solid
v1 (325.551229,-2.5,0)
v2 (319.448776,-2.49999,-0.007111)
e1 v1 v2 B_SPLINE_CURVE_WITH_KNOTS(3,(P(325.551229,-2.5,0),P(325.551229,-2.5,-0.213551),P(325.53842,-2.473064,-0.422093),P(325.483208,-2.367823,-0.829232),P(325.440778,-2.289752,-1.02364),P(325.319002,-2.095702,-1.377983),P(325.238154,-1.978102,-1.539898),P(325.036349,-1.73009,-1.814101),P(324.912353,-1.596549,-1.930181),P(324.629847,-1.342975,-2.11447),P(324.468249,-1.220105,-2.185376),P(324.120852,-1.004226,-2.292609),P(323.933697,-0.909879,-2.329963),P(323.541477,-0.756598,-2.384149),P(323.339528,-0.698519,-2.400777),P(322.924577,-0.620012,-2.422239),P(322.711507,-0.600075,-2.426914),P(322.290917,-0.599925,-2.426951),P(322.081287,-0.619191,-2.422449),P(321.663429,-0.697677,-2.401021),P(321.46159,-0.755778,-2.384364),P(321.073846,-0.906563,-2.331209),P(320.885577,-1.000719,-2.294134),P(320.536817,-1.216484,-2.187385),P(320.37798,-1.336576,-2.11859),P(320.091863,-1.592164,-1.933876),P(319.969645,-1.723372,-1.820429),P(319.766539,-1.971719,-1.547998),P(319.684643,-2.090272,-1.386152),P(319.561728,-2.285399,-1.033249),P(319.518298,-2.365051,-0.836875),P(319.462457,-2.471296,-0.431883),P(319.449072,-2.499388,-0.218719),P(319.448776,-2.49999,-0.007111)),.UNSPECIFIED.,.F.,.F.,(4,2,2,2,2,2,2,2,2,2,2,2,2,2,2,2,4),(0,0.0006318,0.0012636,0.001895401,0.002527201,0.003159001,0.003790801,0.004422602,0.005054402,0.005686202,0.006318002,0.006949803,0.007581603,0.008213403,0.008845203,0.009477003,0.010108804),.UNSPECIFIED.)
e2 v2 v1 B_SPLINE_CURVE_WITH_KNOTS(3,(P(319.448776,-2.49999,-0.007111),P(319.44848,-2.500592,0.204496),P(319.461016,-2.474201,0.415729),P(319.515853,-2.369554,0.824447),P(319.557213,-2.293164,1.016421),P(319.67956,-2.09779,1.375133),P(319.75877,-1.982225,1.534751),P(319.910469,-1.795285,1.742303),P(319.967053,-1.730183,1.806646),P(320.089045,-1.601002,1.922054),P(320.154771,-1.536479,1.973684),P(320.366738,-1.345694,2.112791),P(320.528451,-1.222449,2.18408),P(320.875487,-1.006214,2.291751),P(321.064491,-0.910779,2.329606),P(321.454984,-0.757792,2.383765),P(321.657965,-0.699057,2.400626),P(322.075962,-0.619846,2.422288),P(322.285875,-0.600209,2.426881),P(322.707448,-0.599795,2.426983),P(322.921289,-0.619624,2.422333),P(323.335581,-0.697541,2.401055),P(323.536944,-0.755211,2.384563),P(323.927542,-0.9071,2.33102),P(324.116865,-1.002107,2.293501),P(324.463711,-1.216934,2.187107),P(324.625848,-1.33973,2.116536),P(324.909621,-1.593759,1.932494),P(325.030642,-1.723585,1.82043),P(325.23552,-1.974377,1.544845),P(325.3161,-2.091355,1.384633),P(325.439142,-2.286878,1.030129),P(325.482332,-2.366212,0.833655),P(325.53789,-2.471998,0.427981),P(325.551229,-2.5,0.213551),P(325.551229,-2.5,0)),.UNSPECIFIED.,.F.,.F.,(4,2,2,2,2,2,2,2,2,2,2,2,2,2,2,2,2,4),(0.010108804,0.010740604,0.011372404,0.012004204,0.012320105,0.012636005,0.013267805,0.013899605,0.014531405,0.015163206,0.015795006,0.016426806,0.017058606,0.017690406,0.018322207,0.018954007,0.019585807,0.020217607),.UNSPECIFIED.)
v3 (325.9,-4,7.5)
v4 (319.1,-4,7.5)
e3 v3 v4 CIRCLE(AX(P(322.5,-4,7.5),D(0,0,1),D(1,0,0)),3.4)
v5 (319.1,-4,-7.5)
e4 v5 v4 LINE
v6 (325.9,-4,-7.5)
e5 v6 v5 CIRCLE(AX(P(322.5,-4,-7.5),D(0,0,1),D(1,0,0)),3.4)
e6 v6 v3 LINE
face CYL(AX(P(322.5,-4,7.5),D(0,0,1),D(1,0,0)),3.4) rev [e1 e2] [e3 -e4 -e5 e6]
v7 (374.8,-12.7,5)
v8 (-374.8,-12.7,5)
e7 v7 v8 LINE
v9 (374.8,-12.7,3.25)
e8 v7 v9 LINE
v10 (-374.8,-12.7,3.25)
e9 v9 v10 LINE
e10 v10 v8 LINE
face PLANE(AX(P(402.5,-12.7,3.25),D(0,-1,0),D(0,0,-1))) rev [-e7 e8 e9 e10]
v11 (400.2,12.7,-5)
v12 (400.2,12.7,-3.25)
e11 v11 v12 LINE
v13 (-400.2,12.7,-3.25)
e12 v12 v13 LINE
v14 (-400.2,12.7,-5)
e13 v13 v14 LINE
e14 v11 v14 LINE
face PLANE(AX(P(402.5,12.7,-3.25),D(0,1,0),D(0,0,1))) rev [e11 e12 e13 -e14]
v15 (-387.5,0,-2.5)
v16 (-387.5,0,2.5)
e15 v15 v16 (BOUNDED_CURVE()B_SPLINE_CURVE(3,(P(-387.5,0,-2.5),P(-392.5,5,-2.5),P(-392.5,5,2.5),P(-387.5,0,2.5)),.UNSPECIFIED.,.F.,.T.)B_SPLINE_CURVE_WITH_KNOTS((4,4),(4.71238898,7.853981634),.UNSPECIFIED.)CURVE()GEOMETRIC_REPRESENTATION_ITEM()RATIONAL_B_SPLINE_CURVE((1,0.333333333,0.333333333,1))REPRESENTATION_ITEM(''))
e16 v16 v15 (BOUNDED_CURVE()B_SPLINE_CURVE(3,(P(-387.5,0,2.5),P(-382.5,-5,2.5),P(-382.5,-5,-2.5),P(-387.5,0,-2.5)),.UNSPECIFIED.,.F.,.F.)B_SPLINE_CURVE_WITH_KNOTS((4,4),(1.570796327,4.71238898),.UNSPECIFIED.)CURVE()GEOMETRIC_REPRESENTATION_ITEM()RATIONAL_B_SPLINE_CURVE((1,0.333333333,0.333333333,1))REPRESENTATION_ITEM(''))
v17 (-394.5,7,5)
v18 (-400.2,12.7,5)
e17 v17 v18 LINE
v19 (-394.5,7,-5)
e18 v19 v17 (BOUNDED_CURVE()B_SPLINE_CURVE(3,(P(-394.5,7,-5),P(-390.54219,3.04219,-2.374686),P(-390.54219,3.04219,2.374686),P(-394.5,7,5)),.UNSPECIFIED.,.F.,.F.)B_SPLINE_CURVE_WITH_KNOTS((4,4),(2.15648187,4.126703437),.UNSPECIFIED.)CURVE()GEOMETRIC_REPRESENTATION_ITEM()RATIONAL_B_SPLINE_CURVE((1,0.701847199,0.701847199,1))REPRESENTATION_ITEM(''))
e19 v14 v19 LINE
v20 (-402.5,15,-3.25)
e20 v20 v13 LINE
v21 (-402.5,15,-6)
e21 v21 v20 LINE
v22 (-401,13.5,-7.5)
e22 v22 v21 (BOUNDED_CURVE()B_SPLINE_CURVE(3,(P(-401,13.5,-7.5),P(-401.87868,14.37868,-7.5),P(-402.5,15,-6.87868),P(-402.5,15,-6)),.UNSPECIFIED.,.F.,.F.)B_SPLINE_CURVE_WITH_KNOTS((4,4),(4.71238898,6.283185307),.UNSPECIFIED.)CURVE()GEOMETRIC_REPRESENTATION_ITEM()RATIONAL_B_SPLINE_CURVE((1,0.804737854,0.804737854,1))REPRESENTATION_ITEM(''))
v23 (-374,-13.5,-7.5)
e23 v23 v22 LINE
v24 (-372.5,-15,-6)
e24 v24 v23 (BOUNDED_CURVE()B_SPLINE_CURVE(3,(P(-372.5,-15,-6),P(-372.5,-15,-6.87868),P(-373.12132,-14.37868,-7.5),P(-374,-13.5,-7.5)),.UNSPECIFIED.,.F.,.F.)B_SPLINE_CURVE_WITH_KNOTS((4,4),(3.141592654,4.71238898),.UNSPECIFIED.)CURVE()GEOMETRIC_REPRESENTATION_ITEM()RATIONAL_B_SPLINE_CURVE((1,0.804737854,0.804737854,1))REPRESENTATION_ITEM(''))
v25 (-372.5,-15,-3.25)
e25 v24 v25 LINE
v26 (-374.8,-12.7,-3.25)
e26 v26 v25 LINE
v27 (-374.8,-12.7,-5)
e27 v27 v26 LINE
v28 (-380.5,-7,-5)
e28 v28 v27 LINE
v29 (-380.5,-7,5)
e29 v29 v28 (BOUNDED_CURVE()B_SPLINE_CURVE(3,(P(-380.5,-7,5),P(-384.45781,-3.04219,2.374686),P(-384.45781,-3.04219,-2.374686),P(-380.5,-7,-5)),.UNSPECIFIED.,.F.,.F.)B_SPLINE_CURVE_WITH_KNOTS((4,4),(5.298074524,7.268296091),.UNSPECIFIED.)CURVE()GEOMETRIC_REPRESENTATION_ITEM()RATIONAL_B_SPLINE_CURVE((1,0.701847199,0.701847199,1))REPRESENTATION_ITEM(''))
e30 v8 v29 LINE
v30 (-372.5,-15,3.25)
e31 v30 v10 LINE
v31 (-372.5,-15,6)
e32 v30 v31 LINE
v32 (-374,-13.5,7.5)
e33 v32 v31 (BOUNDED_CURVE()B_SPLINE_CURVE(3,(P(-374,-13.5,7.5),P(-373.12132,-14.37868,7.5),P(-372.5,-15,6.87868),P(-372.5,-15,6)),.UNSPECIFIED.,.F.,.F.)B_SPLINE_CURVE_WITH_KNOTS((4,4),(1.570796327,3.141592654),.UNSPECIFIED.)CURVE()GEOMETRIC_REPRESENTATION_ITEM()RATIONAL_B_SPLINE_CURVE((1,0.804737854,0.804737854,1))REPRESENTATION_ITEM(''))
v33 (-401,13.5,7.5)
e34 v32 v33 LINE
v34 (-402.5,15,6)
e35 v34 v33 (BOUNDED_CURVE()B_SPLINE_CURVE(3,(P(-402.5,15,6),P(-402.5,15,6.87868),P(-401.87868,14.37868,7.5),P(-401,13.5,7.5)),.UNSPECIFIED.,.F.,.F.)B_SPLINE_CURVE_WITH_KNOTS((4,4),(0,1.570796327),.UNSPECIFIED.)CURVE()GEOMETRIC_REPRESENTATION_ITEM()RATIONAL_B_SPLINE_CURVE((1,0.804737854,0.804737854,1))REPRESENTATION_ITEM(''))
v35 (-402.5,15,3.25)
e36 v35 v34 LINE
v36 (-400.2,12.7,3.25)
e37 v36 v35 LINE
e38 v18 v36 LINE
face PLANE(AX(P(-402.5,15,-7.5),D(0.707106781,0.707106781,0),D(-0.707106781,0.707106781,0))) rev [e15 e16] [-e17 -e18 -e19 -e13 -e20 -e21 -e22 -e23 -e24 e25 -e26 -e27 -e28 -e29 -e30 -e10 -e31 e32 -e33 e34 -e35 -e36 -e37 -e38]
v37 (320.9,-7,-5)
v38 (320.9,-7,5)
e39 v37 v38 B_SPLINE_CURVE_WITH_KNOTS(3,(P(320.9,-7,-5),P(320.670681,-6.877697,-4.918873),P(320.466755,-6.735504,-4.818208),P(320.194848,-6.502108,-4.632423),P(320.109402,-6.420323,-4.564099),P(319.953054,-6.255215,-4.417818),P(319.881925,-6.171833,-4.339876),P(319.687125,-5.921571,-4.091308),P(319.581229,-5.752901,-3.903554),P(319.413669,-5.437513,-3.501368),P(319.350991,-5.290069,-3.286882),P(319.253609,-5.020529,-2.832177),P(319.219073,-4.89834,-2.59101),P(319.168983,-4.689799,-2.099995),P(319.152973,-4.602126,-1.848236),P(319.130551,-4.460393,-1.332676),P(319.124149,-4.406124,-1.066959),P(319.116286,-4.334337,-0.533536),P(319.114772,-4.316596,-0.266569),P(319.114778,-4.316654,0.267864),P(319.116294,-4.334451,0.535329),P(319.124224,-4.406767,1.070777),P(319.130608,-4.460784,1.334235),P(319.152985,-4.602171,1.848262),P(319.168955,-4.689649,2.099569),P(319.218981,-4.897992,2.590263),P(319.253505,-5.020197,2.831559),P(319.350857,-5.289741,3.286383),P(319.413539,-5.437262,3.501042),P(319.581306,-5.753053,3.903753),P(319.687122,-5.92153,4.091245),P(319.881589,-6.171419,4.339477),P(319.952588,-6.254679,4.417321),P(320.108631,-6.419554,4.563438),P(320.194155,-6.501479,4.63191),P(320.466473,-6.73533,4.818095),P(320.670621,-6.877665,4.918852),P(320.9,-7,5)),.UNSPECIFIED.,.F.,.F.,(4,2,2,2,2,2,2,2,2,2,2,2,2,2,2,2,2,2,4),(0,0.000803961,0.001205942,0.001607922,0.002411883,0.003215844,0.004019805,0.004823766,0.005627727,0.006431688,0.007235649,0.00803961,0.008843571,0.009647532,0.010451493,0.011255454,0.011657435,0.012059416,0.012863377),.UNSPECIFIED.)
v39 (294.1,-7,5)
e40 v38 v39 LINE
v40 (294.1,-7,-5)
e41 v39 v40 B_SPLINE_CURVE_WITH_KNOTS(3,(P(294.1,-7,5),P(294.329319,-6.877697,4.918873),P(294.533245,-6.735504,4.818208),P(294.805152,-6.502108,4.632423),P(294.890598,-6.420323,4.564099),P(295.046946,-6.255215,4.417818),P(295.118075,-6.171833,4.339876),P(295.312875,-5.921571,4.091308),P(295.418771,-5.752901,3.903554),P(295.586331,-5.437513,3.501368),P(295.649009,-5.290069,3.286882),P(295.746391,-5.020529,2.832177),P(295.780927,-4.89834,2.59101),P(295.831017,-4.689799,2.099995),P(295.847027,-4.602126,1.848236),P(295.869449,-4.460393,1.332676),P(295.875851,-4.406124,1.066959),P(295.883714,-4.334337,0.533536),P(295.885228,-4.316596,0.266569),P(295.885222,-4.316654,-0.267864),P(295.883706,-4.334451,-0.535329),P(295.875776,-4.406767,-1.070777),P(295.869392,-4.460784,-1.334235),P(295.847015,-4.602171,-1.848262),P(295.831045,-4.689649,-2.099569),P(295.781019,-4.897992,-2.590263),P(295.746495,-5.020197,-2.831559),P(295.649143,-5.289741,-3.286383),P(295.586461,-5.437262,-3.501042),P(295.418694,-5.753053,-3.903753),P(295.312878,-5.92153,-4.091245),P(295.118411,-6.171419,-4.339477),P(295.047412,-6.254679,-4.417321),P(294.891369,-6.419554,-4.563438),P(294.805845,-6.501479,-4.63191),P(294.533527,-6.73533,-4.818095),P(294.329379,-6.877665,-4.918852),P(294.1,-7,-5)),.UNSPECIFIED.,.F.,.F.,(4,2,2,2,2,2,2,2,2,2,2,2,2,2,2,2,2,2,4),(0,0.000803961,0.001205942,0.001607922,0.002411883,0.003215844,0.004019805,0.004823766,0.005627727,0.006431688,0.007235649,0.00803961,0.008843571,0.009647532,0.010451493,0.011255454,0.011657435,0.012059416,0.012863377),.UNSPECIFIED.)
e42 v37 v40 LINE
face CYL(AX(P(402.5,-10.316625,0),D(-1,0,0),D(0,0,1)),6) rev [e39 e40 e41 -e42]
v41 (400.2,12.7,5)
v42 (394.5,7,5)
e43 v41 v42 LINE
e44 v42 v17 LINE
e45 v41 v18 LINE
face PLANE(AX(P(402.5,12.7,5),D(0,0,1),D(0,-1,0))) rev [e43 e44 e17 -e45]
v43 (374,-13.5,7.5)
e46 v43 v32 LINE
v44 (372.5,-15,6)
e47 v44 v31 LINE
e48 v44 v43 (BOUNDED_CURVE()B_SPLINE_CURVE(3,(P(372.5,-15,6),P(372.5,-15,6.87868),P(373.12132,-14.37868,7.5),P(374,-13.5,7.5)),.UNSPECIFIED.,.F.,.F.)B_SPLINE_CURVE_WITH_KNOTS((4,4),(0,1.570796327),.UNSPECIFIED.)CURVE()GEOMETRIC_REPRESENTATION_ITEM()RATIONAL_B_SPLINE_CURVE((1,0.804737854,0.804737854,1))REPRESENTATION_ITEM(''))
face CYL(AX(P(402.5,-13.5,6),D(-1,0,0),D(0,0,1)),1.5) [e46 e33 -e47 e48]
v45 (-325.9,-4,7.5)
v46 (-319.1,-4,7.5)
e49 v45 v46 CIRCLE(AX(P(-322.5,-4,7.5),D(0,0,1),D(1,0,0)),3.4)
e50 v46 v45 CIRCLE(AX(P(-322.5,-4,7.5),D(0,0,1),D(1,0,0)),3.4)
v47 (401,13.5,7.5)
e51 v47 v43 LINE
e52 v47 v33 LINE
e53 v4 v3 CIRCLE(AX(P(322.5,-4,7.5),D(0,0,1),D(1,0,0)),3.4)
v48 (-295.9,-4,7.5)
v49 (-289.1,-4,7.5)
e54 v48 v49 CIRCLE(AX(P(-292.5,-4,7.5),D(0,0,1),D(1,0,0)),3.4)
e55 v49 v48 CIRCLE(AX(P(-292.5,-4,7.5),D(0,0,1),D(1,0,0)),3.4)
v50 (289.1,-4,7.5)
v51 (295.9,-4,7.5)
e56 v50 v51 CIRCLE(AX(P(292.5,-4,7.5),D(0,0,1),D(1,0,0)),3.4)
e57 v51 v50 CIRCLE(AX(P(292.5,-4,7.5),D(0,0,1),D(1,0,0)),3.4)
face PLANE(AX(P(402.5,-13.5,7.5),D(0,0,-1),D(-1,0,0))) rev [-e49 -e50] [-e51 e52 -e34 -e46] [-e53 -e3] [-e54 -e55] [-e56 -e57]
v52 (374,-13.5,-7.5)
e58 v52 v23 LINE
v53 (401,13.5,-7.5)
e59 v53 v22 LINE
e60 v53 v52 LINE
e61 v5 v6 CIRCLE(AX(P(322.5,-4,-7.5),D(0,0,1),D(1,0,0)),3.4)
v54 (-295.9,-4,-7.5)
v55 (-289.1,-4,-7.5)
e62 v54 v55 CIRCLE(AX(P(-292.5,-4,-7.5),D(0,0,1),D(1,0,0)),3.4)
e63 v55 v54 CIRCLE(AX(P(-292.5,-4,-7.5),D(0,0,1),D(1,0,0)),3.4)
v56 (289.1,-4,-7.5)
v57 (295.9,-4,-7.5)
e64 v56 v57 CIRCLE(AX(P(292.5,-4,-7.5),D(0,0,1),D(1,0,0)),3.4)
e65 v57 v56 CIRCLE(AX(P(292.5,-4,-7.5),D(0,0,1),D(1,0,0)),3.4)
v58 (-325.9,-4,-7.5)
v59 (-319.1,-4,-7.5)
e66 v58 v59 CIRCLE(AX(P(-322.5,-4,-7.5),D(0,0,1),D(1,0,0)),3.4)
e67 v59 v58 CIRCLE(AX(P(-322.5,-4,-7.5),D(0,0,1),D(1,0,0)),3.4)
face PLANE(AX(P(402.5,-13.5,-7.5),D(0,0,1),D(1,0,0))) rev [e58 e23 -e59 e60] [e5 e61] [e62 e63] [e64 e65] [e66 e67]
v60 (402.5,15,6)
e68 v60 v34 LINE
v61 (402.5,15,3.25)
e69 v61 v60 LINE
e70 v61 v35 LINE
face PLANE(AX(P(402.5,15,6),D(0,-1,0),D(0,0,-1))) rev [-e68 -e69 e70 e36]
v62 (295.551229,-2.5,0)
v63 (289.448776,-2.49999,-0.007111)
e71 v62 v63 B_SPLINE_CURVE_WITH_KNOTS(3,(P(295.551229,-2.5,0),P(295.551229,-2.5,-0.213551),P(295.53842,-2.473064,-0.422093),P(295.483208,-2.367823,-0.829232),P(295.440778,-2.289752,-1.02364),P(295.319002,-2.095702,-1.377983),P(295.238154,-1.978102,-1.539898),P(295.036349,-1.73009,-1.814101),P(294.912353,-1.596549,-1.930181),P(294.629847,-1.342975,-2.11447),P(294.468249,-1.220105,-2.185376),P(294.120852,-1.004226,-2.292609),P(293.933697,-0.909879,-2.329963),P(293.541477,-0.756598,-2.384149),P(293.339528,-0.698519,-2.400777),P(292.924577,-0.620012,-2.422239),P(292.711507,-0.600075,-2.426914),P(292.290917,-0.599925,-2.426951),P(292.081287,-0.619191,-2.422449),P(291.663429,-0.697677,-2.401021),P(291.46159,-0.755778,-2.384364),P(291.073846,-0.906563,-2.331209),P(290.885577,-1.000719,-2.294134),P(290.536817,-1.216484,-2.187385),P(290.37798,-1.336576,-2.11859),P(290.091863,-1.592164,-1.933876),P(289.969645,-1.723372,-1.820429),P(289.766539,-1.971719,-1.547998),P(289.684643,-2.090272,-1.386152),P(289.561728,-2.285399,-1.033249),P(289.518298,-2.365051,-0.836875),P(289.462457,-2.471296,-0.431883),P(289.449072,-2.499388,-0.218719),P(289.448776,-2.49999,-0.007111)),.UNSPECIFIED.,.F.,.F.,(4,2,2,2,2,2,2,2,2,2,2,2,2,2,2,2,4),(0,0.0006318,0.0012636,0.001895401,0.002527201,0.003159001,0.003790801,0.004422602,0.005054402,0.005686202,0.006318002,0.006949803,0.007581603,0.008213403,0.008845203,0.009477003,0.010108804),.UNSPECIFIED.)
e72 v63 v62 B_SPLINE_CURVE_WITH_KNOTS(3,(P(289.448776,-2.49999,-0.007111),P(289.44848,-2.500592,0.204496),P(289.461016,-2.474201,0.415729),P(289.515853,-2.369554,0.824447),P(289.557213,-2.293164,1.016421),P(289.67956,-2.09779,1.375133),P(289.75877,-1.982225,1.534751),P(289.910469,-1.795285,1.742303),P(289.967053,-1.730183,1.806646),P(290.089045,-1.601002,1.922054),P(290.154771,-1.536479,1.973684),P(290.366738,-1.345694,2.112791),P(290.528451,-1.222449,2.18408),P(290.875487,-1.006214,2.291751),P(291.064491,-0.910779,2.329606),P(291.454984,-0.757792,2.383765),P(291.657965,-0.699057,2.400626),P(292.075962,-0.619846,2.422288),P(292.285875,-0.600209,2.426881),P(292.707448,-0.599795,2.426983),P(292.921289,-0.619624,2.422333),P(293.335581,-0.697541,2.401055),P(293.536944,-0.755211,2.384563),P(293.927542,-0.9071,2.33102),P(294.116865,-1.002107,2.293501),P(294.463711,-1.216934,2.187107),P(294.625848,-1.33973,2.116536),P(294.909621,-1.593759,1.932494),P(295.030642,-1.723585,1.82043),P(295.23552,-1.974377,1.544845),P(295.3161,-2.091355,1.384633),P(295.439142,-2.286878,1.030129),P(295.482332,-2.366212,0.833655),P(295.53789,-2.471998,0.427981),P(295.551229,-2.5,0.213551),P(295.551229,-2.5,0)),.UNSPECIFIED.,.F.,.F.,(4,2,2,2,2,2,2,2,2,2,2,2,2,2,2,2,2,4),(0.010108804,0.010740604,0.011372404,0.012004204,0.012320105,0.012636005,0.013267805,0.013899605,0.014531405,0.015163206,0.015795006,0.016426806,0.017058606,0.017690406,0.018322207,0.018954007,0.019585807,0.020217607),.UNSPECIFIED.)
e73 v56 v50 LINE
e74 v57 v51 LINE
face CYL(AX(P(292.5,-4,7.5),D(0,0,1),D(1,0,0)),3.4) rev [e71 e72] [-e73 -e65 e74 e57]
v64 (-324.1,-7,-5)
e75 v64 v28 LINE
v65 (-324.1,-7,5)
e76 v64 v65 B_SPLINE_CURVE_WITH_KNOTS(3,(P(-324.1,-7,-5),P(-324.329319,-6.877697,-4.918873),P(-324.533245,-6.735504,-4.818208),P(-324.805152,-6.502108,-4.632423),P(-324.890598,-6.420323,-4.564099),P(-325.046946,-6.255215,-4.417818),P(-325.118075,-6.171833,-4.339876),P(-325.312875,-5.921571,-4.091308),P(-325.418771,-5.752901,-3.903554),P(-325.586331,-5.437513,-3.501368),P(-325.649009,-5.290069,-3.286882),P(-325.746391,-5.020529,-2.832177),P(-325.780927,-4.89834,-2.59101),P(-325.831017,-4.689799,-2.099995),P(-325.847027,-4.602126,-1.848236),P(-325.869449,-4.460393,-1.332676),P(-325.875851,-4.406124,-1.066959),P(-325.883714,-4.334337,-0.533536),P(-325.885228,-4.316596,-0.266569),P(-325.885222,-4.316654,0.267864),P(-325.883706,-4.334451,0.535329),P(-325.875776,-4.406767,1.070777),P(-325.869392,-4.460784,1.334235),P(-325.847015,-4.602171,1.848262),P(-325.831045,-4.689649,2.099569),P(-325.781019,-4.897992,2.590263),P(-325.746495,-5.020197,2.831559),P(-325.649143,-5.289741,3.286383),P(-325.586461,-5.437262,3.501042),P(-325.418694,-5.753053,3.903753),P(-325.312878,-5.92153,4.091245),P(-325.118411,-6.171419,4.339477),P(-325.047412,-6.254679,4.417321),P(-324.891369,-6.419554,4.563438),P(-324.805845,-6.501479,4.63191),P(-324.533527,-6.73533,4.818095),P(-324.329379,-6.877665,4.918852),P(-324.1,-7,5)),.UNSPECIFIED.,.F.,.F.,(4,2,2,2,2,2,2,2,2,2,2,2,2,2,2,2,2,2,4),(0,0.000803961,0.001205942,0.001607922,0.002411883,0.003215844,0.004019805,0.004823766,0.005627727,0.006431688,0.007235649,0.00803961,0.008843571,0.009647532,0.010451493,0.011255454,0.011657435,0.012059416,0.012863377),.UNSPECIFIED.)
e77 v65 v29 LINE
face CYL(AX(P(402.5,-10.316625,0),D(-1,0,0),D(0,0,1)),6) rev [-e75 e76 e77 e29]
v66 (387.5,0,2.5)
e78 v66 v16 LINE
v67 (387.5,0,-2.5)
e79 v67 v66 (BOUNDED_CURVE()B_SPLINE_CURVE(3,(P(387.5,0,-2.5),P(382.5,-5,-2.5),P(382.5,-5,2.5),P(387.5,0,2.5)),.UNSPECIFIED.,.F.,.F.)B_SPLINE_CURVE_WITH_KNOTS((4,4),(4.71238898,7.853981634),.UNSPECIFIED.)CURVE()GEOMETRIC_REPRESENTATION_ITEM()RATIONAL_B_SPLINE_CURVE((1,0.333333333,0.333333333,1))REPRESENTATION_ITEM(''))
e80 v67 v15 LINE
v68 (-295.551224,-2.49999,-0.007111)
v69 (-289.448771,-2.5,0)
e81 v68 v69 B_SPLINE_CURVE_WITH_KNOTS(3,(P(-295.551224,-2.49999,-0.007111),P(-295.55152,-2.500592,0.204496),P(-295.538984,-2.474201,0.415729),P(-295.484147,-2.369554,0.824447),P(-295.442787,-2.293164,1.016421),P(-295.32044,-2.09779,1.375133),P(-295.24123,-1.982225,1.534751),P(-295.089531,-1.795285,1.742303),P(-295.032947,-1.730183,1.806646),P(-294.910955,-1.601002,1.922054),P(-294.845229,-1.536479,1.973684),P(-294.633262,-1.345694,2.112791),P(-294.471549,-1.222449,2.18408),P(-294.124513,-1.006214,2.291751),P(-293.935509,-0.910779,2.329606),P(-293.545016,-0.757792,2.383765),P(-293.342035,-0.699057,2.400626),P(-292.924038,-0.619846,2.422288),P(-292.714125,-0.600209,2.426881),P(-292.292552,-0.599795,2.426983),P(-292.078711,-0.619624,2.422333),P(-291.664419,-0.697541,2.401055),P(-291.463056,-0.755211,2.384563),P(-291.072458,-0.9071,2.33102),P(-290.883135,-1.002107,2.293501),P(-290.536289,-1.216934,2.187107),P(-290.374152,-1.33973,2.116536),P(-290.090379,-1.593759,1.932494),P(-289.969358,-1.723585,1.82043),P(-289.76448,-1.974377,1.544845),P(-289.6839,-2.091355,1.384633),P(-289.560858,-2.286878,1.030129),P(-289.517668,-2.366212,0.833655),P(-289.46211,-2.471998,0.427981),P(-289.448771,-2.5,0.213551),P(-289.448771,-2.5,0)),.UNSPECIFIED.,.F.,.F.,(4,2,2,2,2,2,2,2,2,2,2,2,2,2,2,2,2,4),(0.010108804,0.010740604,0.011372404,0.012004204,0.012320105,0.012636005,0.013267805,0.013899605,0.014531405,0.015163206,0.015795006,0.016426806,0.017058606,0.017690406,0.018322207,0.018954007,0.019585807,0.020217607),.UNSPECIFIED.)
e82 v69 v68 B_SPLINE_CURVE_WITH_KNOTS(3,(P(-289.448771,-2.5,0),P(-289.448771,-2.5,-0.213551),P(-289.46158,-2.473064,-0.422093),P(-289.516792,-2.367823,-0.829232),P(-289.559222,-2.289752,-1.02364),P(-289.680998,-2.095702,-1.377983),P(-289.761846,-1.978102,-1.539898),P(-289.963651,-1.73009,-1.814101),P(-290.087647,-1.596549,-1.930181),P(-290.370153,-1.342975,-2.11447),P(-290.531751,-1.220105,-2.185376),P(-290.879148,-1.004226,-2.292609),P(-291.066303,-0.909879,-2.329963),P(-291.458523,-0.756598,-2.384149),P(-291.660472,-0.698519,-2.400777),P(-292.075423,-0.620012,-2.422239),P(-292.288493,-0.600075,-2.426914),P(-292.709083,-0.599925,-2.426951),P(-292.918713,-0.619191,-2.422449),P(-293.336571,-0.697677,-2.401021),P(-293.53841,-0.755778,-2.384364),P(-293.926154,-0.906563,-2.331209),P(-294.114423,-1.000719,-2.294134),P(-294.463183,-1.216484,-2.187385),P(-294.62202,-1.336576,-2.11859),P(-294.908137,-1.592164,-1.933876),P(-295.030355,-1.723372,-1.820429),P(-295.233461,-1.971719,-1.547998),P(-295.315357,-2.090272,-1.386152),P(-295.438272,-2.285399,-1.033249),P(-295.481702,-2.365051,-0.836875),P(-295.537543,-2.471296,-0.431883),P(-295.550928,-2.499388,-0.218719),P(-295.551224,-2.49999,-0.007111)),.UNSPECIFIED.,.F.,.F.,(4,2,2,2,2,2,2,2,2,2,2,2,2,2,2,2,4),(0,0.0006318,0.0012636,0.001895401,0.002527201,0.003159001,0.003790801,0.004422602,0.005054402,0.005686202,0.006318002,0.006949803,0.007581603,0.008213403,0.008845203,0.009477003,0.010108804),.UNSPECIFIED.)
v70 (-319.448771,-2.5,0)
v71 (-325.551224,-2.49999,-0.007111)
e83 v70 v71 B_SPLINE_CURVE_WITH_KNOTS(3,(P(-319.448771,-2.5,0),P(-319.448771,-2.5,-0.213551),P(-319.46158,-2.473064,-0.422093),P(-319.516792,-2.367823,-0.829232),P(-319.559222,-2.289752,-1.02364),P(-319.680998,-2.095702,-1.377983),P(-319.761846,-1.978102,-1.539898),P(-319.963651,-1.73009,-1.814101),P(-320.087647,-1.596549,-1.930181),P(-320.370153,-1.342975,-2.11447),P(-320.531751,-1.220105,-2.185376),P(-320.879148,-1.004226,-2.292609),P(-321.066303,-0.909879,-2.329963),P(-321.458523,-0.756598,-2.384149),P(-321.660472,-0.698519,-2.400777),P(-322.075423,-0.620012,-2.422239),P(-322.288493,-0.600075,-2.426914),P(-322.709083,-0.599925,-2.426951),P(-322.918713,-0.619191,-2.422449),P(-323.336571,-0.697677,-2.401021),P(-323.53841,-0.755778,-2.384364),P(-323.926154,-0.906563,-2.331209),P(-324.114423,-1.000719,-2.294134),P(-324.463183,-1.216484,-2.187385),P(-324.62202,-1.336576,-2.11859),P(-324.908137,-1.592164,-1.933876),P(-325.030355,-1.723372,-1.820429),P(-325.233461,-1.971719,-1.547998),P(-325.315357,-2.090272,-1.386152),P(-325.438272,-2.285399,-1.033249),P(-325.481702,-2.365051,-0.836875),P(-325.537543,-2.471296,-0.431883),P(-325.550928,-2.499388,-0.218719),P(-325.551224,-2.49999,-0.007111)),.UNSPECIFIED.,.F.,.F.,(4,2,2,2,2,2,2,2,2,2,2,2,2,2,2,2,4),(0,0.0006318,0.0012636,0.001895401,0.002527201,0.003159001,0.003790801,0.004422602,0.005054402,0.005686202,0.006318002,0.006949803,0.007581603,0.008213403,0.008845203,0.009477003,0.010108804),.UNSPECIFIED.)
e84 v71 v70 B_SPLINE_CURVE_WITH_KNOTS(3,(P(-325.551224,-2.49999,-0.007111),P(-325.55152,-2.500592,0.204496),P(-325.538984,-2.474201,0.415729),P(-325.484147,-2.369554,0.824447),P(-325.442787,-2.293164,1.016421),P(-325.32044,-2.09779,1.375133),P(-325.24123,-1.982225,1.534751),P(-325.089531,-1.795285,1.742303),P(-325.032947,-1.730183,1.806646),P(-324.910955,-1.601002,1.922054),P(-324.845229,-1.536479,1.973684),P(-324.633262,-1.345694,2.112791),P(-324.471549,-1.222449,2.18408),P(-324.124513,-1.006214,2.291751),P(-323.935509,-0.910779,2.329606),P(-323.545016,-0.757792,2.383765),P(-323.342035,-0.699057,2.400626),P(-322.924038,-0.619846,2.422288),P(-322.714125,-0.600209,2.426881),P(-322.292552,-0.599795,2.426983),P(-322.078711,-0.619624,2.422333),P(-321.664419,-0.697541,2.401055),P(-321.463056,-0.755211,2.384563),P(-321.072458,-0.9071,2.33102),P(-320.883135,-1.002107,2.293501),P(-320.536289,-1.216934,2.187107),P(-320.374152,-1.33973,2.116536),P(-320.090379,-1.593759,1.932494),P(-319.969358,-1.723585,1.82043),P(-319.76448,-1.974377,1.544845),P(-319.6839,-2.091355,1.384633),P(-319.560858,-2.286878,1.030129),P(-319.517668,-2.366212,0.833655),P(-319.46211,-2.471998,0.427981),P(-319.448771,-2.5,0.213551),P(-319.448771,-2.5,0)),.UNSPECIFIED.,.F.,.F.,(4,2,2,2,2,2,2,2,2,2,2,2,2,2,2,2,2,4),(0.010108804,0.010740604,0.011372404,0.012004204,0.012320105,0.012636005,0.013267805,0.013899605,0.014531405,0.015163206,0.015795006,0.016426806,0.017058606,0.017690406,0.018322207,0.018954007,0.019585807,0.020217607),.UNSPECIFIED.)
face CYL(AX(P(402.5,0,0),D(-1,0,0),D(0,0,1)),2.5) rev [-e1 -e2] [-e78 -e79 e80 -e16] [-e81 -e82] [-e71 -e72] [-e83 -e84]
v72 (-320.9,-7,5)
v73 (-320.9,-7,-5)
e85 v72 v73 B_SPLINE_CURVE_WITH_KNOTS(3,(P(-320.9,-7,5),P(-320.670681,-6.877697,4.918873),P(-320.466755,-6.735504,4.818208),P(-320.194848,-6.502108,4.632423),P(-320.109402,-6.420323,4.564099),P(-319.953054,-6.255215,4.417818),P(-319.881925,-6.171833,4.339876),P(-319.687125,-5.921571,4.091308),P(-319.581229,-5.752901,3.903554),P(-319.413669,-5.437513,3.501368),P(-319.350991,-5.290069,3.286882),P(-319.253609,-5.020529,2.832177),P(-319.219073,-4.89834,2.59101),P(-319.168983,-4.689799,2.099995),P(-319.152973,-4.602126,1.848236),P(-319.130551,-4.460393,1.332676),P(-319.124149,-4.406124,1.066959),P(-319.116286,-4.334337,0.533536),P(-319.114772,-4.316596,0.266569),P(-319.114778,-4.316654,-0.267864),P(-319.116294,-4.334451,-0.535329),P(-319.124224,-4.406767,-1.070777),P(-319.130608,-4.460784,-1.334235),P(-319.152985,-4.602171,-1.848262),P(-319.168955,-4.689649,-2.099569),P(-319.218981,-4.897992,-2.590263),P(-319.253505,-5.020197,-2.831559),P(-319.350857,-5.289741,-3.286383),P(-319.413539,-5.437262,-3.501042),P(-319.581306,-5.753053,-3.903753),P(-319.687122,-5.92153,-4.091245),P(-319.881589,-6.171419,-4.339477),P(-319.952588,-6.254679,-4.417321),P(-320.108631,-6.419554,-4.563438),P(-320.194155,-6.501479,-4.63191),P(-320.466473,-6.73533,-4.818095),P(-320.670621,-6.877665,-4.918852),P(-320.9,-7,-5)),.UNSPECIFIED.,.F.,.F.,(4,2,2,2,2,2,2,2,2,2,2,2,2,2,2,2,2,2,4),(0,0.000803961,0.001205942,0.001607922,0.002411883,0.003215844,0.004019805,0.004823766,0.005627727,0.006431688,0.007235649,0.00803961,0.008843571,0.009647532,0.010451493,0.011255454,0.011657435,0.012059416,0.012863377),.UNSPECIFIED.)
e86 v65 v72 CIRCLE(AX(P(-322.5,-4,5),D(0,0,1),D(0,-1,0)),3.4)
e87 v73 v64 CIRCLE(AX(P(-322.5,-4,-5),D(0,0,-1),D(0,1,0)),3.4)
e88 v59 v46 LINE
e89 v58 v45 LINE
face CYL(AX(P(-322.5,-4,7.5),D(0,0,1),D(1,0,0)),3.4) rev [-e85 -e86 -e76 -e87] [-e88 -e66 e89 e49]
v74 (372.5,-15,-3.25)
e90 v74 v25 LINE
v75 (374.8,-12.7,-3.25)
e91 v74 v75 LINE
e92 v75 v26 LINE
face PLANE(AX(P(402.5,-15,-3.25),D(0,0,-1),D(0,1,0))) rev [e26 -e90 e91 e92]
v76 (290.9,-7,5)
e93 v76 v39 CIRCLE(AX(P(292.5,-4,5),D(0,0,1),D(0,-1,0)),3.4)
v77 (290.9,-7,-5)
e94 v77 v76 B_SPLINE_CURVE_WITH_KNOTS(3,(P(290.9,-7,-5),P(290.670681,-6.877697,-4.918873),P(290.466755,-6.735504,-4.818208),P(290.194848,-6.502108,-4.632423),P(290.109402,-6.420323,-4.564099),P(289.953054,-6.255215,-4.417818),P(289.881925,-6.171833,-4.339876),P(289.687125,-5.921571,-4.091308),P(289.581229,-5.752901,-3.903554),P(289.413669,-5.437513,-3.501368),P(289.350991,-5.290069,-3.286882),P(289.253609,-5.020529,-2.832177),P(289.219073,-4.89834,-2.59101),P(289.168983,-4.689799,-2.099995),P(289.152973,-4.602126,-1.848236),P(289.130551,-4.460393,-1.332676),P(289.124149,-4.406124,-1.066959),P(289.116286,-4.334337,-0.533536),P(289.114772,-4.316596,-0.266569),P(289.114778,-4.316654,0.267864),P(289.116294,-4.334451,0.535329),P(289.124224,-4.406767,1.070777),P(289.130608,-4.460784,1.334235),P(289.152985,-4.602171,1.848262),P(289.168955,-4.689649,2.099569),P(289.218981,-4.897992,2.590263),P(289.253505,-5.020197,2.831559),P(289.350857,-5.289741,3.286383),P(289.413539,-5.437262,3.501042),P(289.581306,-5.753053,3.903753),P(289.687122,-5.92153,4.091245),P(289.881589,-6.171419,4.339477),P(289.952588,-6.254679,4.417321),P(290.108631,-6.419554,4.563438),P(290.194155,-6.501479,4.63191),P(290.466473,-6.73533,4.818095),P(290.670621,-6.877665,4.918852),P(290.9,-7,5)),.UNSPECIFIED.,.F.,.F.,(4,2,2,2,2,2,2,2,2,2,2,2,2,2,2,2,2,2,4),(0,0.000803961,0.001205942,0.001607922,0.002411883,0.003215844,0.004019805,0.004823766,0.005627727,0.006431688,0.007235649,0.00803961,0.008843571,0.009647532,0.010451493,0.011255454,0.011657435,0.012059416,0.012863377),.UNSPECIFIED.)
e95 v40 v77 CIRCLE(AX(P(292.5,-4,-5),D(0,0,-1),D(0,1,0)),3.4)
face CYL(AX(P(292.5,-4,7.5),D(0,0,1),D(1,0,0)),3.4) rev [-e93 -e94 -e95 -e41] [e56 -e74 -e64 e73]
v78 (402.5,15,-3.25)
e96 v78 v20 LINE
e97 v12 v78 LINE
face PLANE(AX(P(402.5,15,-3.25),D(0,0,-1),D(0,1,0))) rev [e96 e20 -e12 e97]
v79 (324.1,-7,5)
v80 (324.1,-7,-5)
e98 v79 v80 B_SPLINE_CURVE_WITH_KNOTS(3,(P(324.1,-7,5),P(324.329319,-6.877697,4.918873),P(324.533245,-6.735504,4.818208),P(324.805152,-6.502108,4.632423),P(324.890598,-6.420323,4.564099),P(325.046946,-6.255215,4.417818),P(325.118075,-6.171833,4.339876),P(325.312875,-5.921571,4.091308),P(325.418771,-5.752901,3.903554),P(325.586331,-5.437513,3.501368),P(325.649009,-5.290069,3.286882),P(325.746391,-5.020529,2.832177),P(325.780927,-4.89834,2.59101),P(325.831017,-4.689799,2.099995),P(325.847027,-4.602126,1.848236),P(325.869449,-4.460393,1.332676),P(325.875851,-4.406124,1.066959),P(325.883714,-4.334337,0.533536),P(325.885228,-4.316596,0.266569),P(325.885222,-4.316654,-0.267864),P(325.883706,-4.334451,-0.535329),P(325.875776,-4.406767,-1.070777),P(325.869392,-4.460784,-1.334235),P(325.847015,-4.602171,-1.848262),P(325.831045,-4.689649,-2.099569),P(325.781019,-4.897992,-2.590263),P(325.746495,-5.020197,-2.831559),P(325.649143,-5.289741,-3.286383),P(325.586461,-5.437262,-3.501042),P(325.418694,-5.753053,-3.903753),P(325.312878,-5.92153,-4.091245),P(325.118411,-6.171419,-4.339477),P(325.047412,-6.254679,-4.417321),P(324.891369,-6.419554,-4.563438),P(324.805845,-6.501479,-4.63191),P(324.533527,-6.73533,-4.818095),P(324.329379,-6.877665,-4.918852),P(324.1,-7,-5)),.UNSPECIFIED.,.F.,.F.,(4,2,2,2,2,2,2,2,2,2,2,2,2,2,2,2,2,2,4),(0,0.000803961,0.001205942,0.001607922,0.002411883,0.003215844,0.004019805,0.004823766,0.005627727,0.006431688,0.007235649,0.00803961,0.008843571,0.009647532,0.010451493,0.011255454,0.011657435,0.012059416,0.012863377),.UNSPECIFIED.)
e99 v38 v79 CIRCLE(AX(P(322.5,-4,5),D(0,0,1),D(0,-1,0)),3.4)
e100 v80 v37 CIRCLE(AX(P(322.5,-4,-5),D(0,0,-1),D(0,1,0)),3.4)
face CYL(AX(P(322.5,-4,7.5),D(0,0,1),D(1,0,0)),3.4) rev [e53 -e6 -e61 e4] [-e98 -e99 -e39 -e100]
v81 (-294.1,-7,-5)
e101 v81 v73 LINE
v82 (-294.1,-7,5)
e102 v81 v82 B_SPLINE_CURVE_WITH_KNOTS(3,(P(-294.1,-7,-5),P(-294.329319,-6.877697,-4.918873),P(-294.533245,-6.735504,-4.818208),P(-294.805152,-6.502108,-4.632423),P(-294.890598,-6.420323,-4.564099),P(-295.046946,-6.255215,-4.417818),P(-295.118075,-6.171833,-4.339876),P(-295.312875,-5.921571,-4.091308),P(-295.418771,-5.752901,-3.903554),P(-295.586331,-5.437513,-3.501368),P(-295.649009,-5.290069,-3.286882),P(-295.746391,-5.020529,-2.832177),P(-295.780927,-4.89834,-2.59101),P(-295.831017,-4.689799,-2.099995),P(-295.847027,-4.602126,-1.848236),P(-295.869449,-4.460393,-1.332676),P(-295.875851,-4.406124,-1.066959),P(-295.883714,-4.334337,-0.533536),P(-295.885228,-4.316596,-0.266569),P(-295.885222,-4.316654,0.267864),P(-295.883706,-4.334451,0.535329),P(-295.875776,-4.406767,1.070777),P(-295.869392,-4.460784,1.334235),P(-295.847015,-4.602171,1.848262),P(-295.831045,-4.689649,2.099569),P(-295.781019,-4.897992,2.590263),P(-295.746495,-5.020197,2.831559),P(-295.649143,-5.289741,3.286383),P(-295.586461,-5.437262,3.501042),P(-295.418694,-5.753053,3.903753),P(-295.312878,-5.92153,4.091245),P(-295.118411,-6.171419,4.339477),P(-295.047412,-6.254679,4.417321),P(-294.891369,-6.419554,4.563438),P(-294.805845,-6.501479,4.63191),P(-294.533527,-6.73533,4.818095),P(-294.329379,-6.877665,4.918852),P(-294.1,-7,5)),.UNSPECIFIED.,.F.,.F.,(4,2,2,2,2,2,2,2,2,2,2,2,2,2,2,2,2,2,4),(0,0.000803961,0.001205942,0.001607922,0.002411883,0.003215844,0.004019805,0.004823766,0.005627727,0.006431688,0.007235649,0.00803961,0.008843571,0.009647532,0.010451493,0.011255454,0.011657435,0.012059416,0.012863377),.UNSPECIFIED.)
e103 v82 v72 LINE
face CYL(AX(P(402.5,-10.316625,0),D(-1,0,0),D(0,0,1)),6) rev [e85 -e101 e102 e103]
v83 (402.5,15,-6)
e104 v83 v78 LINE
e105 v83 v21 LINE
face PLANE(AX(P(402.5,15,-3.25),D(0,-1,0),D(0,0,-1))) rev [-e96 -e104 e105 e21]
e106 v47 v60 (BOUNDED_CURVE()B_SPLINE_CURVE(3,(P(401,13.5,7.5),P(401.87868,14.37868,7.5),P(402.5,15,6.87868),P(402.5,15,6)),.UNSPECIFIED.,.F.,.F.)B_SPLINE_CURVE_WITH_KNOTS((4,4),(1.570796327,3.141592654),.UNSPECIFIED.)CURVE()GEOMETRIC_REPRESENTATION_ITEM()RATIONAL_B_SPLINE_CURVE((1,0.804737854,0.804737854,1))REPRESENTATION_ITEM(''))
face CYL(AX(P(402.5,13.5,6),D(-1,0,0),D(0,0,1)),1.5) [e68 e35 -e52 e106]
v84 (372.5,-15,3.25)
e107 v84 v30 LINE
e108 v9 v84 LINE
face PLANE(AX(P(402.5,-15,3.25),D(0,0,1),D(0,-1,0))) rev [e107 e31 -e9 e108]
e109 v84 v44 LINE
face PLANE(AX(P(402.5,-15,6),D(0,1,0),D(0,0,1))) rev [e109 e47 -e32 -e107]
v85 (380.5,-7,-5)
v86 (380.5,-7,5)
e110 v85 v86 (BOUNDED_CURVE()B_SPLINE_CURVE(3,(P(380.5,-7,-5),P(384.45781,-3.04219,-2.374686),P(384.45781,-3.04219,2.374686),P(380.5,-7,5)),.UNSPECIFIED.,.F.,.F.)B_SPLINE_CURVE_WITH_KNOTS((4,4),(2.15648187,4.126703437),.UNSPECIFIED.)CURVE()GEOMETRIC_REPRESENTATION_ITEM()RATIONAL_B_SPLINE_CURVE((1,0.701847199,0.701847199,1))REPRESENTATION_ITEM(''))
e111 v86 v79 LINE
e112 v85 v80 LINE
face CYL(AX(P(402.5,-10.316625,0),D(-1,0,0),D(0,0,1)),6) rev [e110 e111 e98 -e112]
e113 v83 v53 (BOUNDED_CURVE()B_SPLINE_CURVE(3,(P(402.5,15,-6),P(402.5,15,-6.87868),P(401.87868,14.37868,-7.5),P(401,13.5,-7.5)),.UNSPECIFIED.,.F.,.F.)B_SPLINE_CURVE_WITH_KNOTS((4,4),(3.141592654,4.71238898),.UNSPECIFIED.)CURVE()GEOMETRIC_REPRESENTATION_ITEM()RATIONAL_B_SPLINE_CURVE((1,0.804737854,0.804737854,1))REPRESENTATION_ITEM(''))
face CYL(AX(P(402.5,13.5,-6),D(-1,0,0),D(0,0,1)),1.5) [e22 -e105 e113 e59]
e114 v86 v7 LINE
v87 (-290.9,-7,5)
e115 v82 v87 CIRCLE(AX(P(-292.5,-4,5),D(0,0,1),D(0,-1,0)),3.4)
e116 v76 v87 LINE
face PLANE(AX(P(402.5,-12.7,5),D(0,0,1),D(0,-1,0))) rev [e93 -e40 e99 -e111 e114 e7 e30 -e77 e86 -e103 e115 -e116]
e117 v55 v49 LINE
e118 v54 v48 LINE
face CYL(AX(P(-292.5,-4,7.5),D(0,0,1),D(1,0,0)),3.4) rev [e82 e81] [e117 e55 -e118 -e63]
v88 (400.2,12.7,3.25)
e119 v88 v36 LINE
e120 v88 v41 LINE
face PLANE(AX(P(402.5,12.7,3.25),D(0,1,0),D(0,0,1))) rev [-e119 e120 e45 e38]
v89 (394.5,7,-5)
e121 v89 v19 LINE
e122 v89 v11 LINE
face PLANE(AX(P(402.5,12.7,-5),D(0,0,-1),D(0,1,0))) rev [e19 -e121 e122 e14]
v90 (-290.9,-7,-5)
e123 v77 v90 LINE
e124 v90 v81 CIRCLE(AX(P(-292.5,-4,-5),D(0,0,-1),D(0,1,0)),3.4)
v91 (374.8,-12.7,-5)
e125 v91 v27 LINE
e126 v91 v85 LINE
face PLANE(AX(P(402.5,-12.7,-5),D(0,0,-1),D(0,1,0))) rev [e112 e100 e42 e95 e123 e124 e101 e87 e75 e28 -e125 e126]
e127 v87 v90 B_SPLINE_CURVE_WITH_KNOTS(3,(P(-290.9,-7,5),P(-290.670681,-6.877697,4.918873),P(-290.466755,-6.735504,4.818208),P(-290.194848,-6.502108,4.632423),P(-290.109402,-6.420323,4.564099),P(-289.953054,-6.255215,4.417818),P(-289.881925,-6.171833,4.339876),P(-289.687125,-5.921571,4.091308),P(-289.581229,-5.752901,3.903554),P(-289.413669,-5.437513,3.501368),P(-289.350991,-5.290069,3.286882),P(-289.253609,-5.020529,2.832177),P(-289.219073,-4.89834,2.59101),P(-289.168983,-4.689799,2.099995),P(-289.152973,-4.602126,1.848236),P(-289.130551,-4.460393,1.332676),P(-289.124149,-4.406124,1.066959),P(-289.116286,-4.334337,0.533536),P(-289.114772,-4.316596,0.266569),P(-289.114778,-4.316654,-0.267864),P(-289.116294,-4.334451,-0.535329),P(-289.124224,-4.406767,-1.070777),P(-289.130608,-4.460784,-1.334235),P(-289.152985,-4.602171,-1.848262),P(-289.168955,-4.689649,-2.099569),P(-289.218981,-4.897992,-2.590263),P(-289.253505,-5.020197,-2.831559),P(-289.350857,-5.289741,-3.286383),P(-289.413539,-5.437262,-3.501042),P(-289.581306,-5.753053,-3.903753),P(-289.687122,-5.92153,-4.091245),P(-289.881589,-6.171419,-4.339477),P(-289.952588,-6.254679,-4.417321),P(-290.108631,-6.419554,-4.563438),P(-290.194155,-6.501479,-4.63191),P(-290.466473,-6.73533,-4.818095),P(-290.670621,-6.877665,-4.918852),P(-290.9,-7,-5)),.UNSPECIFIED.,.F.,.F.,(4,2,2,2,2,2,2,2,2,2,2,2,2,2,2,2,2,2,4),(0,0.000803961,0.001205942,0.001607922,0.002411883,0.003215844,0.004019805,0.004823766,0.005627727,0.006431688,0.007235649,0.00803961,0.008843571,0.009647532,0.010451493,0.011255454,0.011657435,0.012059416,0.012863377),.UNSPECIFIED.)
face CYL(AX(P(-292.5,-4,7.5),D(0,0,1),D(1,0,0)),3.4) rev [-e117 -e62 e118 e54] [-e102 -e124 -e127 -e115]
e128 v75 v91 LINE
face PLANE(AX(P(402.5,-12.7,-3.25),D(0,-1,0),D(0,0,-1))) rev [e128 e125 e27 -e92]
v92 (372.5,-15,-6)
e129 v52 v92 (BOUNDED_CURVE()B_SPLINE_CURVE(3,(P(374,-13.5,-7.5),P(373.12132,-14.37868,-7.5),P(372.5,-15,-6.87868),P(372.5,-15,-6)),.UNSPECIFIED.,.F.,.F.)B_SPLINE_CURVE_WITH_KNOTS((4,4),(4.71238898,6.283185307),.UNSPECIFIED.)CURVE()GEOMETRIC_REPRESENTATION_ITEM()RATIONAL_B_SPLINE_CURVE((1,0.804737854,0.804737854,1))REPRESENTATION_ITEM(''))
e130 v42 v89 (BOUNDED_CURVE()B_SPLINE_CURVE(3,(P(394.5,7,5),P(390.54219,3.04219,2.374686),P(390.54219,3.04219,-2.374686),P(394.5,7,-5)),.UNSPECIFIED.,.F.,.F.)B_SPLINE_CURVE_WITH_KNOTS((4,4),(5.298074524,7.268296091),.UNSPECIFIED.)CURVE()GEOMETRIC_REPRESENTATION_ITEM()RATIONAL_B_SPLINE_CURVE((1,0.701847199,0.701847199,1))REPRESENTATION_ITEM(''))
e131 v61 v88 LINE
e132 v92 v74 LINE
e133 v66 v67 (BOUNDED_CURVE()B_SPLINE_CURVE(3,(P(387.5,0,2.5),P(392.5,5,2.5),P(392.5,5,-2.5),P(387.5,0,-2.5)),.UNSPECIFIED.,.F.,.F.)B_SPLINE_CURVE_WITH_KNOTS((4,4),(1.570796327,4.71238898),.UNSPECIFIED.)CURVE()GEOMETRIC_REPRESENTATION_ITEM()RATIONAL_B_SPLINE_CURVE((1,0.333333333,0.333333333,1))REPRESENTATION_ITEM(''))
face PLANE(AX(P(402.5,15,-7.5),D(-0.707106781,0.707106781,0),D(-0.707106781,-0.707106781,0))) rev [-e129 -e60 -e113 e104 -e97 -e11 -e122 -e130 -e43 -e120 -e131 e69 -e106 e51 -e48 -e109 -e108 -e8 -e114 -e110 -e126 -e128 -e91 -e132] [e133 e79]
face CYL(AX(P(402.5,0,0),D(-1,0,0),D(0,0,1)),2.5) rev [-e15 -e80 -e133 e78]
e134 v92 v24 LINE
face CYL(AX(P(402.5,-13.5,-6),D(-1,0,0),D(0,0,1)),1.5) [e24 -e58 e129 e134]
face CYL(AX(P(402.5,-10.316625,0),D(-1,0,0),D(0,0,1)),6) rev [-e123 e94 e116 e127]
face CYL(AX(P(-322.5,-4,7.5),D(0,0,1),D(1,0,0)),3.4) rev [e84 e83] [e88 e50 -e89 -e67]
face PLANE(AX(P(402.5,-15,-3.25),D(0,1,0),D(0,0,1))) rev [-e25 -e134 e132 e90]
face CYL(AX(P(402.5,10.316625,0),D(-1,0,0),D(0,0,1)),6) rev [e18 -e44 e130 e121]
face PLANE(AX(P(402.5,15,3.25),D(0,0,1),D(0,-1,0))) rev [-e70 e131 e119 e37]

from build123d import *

# Parameters (mm, degrees)
SKETCH11_R          = 2.5
MEMBER_1_DEPTH      = 805
CUT_EXTRUDE_1_DEPTH = 404.058618566
HOLE_WIZARD_M8_1_D  = 6.8


with BuildPart() as part:
    # Sketch11 → Member 1 (new body)
    with BuildSketch(Plane(origin=(-402.5, 0, 0), x_dir=(0, 0, -1), z_dir=(1, 0, 0))):
        with BuildLine():
            Line((-6, -15), (-3.25, -15))
            Line((-3.25, -15), (-3.25, -12.7))
            Line((-3.25, -12.7), (-5, -12.7))
            Line((-5, -12.7), (-5, -7))
            ThreePointArc((-5, -7), (0, -4.31662479), (5, -7))
            Line((5, -7), (5, -12.7))
            Line((5, -12.7), (3.25, -12.7))
            Line((3.25, -12.7), (3.25, -15))
            Line((3.25, -15), (6, -15))
            ThreePointArc((6, -15), (7.060660172, -14.560660172), (7.5, -13.5))
            Line((7.5, -13.5), (7.5, 13.5))
            ThreePointArc((7.5, 13.5), (7.060660172, 14.560660172), (6, 15))
            Line((6, 15), (3.25, 15))
            Line((3.25, 15), (3.25, 12.7))
            Line((3.25, 12.7), (5, 12.7))
            Line((5, 12.7), (5, 7))
            ThreePointArc((5, 7), (0, 4.31662479), (-5, 7))
            Line((-5, 7), (-5, 12.7))
            Line((-5, 12.7), (-3.25, 12.7))
            Line((-3.25, 12.7), (-3.25, 15))
            Line((-3.25, 15), (-6, 15))
            ThreePointArc((-6, 15), (-7.060660172, 14.560660172), (-7.5, 13.5))
            Line((-7.5, 13.5), (-7.5, -13.5))
            ThreePointArc((-7.5, -13.5), (-7.060660172, -14.560660172), (-6, -15))
        make_face()
        Circle(SKETCH11_R, mode=Mode.SUBTRACT)
    extrude(amount=MEMBER_1_DEPTH)

    # 草图4 → 切除-拉伸1 (cut, through all)
    with BuildSketch(Plane.XY.offset(7.5)):
        Polygon((-402.5, 15), (-372.5, -15), (-402.5, -15), align=None)
        Polygon((402.5, -15), (402.5, 15), (372.5, -15), align=None)
    extrude(amount=-CUT_EXTRUDE_1_DEPTH, mode=Mode.SUBTRACT)

    # M8 螺纹孔1 (through all)
    with Locations(Plane.XY.offset(7.5)):
        with Locations((-322.5, -4), (-292.5, -4), (292.5, -4), (322.5, -4)):
            Hole(HOLE_WIZARD_M8_1_D / 2)


solid = part.part
